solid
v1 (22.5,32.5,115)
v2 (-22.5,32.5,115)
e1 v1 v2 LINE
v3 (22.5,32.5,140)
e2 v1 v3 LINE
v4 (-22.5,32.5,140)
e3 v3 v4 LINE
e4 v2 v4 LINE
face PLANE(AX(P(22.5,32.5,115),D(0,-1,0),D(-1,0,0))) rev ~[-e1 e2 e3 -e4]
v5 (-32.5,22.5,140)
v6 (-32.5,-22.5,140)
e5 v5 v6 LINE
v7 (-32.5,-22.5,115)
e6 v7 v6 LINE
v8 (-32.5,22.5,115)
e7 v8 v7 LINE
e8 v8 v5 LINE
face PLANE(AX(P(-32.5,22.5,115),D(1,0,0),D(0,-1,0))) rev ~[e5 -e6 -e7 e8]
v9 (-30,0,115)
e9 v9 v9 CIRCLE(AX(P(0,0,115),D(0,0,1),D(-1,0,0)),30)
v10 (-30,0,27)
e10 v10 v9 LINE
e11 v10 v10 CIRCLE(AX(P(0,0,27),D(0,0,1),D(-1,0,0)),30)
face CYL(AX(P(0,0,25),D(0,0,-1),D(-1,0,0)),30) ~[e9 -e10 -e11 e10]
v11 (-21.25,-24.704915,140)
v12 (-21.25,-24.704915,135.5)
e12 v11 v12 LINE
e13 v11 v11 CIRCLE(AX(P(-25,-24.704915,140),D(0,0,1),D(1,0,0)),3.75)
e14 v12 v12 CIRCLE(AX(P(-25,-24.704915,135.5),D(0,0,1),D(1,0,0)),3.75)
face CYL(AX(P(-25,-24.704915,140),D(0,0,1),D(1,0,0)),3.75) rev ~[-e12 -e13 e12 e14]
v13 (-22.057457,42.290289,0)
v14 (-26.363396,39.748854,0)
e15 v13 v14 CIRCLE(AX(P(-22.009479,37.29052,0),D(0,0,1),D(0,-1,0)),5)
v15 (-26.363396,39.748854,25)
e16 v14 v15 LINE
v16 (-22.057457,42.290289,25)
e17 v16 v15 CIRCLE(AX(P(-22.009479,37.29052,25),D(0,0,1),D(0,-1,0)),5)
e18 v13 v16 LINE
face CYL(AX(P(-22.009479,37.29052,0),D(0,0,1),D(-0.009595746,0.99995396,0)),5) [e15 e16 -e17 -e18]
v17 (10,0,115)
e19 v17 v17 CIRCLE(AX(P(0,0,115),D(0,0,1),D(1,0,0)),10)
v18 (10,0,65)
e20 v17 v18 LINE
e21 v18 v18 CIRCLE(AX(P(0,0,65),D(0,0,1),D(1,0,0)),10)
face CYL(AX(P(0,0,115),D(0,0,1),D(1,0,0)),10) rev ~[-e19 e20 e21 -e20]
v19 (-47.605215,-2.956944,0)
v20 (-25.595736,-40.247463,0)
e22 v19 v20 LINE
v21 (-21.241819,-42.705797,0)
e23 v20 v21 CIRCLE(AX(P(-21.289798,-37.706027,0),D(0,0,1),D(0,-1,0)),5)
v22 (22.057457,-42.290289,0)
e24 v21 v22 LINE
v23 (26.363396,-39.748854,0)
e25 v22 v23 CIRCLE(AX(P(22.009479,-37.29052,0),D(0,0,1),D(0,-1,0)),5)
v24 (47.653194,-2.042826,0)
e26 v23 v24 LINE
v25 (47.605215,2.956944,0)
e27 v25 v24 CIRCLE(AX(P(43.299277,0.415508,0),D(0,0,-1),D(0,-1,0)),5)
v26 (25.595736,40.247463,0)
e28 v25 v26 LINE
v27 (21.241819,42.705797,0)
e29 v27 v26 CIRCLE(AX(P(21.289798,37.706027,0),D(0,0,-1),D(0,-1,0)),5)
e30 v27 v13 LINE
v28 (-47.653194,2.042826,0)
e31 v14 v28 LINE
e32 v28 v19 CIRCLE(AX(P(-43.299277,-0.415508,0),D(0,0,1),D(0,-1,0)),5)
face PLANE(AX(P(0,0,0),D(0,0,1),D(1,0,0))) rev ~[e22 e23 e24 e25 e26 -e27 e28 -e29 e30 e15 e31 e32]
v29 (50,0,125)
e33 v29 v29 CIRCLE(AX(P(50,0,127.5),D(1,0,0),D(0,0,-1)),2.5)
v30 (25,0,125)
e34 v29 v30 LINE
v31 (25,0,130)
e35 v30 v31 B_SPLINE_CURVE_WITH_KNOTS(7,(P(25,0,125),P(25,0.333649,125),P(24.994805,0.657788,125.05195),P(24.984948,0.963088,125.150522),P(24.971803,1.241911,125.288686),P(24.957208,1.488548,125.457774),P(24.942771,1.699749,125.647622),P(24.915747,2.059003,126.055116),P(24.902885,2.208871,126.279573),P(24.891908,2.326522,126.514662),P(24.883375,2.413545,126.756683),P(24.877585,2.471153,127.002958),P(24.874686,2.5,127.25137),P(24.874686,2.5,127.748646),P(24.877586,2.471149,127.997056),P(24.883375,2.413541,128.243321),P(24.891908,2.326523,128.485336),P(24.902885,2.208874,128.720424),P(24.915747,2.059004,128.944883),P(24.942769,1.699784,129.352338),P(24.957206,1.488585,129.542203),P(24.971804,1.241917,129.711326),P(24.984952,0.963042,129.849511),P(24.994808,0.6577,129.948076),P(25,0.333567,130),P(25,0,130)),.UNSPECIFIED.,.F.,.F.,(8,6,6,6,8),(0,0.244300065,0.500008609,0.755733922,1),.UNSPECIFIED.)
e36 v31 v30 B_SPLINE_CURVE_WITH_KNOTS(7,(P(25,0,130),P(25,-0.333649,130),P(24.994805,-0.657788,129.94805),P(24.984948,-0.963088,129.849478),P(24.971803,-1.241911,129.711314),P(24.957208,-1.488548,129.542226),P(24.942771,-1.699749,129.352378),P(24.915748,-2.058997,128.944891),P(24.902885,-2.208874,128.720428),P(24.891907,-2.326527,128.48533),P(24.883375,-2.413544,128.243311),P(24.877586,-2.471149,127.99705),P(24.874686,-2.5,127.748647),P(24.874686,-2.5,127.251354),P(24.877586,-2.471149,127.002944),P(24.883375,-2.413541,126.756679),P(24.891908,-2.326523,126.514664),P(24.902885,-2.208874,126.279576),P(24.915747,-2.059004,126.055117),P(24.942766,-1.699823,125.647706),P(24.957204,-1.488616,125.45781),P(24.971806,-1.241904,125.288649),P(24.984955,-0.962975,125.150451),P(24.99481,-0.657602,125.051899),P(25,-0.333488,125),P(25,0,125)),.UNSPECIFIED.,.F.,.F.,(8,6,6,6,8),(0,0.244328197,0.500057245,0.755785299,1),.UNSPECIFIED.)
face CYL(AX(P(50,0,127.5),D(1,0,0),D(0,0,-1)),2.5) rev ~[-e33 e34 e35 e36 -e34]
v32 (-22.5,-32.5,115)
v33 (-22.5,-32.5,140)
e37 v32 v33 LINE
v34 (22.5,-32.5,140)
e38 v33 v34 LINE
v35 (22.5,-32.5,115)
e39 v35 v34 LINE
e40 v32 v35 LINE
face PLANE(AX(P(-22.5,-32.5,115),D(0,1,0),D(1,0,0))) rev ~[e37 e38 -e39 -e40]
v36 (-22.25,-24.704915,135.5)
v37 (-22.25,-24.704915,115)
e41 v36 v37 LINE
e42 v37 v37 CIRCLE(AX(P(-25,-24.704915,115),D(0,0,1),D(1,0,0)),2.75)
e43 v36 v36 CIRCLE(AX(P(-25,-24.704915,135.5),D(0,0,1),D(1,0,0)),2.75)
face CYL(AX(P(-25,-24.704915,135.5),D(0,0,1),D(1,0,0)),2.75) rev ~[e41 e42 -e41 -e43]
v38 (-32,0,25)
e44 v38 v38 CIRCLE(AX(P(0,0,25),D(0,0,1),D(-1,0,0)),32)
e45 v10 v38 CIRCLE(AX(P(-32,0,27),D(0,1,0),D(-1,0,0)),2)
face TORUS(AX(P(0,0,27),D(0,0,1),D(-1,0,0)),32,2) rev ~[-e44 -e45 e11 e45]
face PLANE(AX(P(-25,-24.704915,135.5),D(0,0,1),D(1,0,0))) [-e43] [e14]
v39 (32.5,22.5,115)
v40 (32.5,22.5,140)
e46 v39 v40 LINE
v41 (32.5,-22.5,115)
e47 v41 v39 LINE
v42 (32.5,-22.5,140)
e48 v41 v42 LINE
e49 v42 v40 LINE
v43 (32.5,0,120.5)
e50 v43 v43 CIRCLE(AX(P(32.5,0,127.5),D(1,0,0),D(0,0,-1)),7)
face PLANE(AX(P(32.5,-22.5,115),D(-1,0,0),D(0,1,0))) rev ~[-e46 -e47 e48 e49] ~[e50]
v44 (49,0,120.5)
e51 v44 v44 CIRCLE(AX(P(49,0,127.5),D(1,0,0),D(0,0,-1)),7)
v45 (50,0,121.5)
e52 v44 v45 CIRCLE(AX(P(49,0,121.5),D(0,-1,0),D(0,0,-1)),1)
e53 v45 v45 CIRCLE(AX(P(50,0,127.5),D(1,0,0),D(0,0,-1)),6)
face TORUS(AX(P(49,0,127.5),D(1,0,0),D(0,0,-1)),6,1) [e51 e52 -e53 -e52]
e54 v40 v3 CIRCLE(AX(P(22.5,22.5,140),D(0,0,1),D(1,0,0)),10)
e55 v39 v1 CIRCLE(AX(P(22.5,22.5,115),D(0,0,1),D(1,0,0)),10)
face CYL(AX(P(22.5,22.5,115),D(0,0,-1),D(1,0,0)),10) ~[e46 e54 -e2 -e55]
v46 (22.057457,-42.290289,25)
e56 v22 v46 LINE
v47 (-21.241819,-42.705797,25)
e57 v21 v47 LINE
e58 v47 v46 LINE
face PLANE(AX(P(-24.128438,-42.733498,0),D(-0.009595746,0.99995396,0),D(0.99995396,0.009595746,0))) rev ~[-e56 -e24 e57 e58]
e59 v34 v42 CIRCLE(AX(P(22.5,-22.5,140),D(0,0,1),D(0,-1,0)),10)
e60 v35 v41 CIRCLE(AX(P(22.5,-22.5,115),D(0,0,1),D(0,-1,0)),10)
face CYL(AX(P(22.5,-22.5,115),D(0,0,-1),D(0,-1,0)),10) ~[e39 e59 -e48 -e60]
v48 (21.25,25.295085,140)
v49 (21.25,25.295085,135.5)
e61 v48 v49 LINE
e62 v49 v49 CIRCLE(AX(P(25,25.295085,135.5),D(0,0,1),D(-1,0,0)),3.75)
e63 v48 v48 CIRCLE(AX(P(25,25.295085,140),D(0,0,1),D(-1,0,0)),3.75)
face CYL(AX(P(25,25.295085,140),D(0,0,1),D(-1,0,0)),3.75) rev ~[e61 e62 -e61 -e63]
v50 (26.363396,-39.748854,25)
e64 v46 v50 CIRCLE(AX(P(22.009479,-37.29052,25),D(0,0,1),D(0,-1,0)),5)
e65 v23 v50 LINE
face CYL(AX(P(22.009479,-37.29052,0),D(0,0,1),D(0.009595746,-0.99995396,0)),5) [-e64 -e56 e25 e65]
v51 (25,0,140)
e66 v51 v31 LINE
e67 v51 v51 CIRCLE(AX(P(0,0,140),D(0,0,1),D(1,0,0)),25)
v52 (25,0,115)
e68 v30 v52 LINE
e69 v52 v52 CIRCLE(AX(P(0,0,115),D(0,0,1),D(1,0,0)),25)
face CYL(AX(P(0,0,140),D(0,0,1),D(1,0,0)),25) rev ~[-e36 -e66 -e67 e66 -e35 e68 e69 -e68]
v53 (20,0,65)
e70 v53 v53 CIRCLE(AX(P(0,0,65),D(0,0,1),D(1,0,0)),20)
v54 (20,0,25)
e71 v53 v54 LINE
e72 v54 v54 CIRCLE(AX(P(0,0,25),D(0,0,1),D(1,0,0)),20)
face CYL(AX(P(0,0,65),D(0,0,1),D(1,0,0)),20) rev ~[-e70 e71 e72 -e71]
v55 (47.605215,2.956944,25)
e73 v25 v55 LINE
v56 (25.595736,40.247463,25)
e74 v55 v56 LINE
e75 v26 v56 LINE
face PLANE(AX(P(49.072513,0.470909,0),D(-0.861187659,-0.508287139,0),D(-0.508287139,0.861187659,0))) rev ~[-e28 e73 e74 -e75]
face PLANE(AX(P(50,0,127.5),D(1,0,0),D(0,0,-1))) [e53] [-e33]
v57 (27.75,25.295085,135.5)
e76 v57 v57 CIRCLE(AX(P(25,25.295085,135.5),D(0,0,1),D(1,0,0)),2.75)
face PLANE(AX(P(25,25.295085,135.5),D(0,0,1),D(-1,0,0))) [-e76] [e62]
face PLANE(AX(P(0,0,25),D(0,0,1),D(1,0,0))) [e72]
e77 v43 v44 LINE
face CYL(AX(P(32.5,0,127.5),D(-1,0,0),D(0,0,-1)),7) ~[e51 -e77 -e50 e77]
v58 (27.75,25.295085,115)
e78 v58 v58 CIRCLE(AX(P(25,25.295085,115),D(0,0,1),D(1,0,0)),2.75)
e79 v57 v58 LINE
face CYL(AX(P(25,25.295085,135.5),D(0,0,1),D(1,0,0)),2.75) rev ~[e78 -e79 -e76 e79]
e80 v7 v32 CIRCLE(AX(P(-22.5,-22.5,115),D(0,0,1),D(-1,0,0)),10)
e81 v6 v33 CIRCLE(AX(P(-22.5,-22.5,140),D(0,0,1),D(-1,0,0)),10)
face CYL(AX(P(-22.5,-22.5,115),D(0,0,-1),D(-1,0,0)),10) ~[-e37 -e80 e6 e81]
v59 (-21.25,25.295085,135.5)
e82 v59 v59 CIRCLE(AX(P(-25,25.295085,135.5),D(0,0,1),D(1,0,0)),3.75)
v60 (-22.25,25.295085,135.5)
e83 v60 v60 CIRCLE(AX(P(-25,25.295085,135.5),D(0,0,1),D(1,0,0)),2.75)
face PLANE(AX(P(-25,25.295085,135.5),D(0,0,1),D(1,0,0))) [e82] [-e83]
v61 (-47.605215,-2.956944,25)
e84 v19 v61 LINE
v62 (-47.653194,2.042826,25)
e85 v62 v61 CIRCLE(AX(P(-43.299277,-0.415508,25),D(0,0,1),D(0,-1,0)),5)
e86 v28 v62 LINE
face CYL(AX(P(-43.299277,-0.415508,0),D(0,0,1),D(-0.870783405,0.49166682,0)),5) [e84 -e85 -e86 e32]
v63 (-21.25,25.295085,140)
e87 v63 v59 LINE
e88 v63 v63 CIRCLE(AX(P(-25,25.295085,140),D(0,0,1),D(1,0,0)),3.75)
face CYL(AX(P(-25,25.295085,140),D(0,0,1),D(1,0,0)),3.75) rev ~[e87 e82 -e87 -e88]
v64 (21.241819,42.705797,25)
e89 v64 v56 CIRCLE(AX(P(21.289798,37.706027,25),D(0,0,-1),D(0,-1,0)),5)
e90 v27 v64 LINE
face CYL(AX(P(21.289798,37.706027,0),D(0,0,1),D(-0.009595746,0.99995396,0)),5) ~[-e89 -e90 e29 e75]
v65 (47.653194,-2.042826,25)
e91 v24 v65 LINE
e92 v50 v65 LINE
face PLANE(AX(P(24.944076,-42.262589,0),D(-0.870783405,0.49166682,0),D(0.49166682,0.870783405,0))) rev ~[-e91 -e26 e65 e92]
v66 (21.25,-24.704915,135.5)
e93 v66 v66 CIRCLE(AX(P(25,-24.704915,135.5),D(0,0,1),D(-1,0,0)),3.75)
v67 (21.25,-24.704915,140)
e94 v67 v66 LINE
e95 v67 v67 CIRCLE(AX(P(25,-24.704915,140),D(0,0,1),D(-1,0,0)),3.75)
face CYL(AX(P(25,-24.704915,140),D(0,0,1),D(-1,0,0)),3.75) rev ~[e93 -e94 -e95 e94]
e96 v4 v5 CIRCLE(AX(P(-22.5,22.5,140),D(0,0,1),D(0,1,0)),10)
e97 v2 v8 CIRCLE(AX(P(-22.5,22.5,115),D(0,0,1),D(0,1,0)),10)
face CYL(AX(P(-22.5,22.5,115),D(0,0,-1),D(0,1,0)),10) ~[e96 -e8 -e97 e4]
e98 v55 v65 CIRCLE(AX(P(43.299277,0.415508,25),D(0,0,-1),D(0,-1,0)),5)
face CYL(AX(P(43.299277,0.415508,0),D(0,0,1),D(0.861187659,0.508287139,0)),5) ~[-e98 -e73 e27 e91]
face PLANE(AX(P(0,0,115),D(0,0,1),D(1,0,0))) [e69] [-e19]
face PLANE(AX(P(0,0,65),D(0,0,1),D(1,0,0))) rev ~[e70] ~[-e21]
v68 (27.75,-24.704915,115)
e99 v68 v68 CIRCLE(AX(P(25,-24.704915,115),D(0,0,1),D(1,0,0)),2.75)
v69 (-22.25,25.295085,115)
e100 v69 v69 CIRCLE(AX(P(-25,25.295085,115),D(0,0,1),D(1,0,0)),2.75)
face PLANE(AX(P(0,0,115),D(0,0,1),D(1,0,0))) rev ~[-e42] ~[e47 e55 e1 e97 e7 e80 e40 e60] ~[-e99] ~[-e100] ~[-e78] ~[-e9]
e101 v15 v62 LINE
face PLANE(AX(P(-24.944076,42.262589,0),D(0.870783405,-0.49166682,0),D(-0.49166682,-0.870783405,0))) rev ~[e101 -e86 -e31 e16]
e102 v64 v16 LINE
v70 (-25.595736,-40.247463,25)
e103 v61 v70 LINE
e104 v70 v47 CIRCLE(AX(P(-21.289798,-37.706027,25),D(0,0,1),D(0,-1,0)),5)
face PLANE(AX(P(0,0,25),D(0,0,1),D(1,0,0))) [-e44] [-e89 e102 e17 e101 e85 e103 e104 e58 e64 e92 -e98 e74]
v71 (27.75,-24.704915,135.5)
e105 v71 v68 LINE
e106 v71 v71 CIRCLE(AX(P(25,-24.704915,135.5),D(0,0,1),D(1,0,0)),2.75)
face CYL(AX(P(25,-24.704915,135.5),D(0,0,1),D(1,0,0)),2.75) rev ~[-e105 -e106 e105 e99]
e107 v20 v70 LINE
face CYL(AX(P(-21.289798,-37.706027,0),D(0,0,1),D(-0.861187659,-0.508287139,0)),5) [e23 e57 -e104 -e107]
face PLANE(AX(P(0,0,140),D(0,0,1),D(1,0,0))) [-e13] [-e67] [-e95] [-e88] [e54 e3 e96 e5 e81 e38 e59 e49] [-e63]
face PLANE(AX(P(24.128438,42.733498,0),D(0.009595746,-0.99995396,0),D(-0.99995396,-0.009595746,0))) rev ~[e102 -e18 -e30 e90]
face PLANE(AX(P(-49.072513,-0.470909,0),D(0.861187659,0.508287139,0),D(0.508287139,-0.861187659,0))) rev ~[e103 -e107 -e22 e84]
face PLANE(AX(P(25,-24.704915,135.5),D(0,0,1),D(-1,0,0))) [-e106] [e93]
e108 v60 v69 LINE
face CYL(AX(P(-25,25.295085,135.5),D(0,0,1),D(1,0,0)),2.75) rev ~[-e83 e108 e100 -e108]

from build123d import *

# Parameters (mm, degrees)
HEX_BODY_DEPTH                     = 25
BODY_PROFILE_60_R                  = 30
BODY_CYLINDER_60_DEPTH             = 90
SQUARE_FLANGE_DEPTH                = 25
FLANGE_BORE_PROFILE_50_R           = 25
FLANGE_BORE_50_DEPTH               = 25
THROUGH_BORE_PROFILE_20_R          = 10
THROUGH_BORE_20_DEPTH              = 50
HEX_END_BORE_PROFILE_40_R          = 20
HEX_END_BORE_40_DEPTH              = 40
HEX_EDGE_FILLET_R5_A_R             = 5
HEX_EDGE_FILLET_R5_B_R             = 5
HEX_EDGE_FILLET_R5_C_R             = 5
HEX_EDGE_FILLET_R5_D_R             = 5
HEX_EDGE_FILLET_R5_E_R             = 5
HEX_EDGE_FILLET_R5_F_R             = 5
COUNTERBORE_PROFILE_4X_7_5_R       = 3.75
MOUNTING_COUNTERBORES_4X_7_5_DEPTH = 4.5
MOUNTING_HOLE_PROFILE_4X_5_5_R     = 2.75
MOUNTING_HOLES_4X_5_5_DEPTH        = 20.5
PORT_BOSS_PROFILE_14_R             = 7
PRESSURE_PORT_BOSS_14_DEPTH        = 17.5
PORT_BOSS_TIP_FILLET_R1_R          = 1
PORT_HOLE_PROFILE_5_R              = 2.5
PORT_HOLE_5_DEPTH                  = 28
BODY_TO_HEX_FILLET_R2_R            = 2


with BuildPart() as part:
    # Hex Profile → Hex Body (new body)
    with BuildSketch(Plane.XY):
        Polygon((24.12843754, 42.733497812), (-24.944075927, 42.262588769), (-49.072513467, -0.470909043), (-24.12843754, -42.733497812), (24.944075927, -42.262588769), (49.072513467, 0.470909043), align=None)
    extrude(amount=HEX_BODY_DEPTH)

    # Body Profile Ø60 → Body Cylinder Ø60 (add)
    with BuildSketch(Plane.XY.offset(25)):
        with Locations(Location((0, 0, 0), (0, 0, 180))):
            Circle(BODY_PROFILE_60_R)
    extrude(amount=BODY_CYLINDER_60_DEPTH)

    # Flange Profile 65x65 → Square Flange (add)
    with BuildSketch(Plane.XY.offset(115)):
        with BuildLine():
            Line((-22.5, -32.5), (22.5, -32.5))
            ThreePointArc((22.5, -32.5), (29.571067812, -29.571067812), (32.5, -22.5))
            Line((32.5, -22.5), (32.5, 22.5))
            ThreePointArc((32.5, 22.5), (29.571067812, 29.571067812), (22.5, 32.5))
            Line((22.5, 32.5), (-22.5, 32.5))
            ThreePointArc((-22.5, 32.5), (-29.571067812, 29.571067812), (-32.5, 22.5))
            Line((-32.5, 22.5), (-32.5, -22.5))
            ThreePointArc((-32.5, -22.5), (-29.571067812, -29.571067812), (-22.5, -32.5))
        make_face()
    extrude(amount=SQUARE_FLANGE_DEPTH)

    # Flange Bore Profile Ø50 → Flange Bore Ø50 (cut)
    with BuildSketch(Plane.XY.offset(140)):
        Circle(FLANGE_BORE_PROFILE_50_R)
    extrude(amount=-FLANGE_BORE_50_DEPTH, mode=Mode.SUBTRACT)

    # Through Bore Profile Ø20 → Through Bore Ø20 (cut)
    with BuildSketch(Plane.XY.offset(115)):
        Circle(THROUGH_BORE_PROFILE_20_R)
    extrude(amount=-THROUGH_BORE_20_DEPTH, mode=Mode.SUBTRACT)

    # Hex End Bore Profile Ø40 → Hex End Bore Ø40 (cut)
    with BuildSketch(Plane.XY.offset(65)):
        Circle(HEX_END_BORE_PROFILE_40_R)
    extrude(amount=-HEX_END_BORE_40_DEPTH, mode=Mode.SUBTRACT)

    # Hex Edge Fillet R5 A
    hex_edge_fillet_r5_a_edges = [part.edges().sort_by_distance(p)[0] for p in [
        (24.12843754, 42.733497812, 12.5),
    ]]
    fillet(hex_edge_fillet_r5_a_edges, radius=HEX_EDGE_FILLET_R5_A_R)

    # Hex Edge Fillet R5 B
    hex_edge_fillet_r5_b_edges = [part.edges().sort_by_distance(p)[0] for p in [
        (49.072513467, 0.470909043, 12.5),
    ]]
    fillet(hex_edge_fillet_r5_b_edges, radius=HEX_EDGE_FILLET_R5_B_R)

    # Hex Edge Fillet R5 C
    hex_edge_fillet_r5_c_edges = [part.edges().sort_by_distance(p)[0] for p in [
        (-24.944075927, 42.262588769, 12.5),
    ]]
    fillet(hex_edge_fillet_r5_c_edges, radius=HEX_EDGE_FILLET_R5_C_R)

    # Hex Edge Fillet R5 D
    hex_edge_fillet_r5_d_edges = [part.edges().sort_by_distance(p)[0] for p in [
        (-49.072513467, -0.470909043, 12.5),
    ]]
    fillet(hex_edge_fillet_r5_d_edges, radius=HEX_EDGE_FILLET_R5_D_R)

    # Hex Edge Fillet R5 E
    hex_edge_fillet_r5_e_edges = [part.edges().sort_by_distance(p)[0] for p in [
        (-24.12843754, -42.733497812, 12.5),
    ]]
    fillet(hex_edge_fillet_r5_e_edges, radius=HEX_EDGE_FILLET_R5_E_R)

    # Hex Edge Fillet R5 F
    hex_edge_fillet_r5_f_edges = [part.edges().sort_by_distance(p)[0] for p in [
        (24.944075927, -42.262588769, 12.5),
    ]]
    fillet(hex_edge_fillet_r5_f_edges, radius=HEX_EDGE_FILLET_R5_F_R)

    # Counterbore Profile 4xØ7.5 → Mounting Counterbores 4xØ7.5 (cut)
    with BuildSketch(Plane.XY.offset(140)):
        with Locations((-25, 25.295084972)):
            Circle(COUNTERBORE_PROFILE_4X_7_5_R)
        with Locations((-25, -24.704915028)):
            Circle(COUNTERBORE_PROFILE_4X_7_5_R)
        with Locations(Location((25, -24.704915028, 0), (0, 0, 180))):
            Circle(COUNTERBORE_PROFILE_4X_7_5_R)
        with Locations(Location((25, 25.295084972, 0), (0, 0, 180))):
            Circle(COUNTERBORE_PROFILE_4X_7_5_R)
    extrude(amount=-MOUNTING_COUNTERBORES_4X_7_5_DEPTH, mode=Mode.SUBTRACT)

    # Mounting Hole Profile 4xØ5.5 → Mounting Holes 4xØ5.5 (cut)
    with BuildSketch(Plane.XY.offset(135.5)):
        with Locations((-25, 25.295084972)):
            Circle(MOUNTING_HOLE_PROFILE_4X_5_5_R)
        with Locations((25, 25.295084972)):
            Circle(MOUNTING_HOLE_PROFILE_4X_5_5_R)
        with Locations((25, -24.704915028)):
            Circle(MOUNTING_HOLE_PROFILE_4X_5_5_R)
        with Locations((-25, -24.704915028)):
            Circle(MOUNTING_HOLE_PROFILE_4X_5_5_R)
    extrude(amount=-MOUNTING_HOLES_4X_5_5_DEPTH, mode=Mode.SUBTRACT)

    # Port Boss Profile Ø14 → Pressure Port Boss Ø14 (add)
    with BuildSketch(Plane(origin=(32.5, 0, 0), x_dir=(0, 0, -1), z_dir=(1, 0, 0))):
        with Locations((-127.5, 0)):
            Circle(PORT_BOSS_PROFILE_14_R)
    extrude(amount=PRESSURE_PORT_BOSS_14_DEPTH)

    # Port Boss Tip Fillet R1
    port_boss_tip_fillet_r1_edges = [part.edges().sort_by_distance(p)[0] for p in [
        (50, 0, 134.5),
    ]]
    fillet(port_boss_tip_fillet_r1_edges, radius=PORT_BOSS_TIP_FILLET_R1_R)

    # Port Hole Profile Ø5 → Port Hole Ø5 (cut)
    with BuildSketch(Plane(origin=(50, 0, 0), x_dir=(0, 0, -1), z_dir=(1, 0, 0))):
        with Locations((-127.5, 0)):
            Circle(PORT_HOLE_PROFILE_5_R)
    extrude(amount=-PORT_HOLE_5_DEPTH, mode=Mode.SUBTRACT)

    # Body to Hex Fillet R2
    body_to_hex_fillet_r2_edges = [part.edges().sort_by_distance(p)[0] for p in [
        (30, 0, 25),
    ]]
    fillet(body_to_hex_fillet_r2_edges, radius=BODY_TO_HEX_FILLET_R2_R)


solid = part.part
